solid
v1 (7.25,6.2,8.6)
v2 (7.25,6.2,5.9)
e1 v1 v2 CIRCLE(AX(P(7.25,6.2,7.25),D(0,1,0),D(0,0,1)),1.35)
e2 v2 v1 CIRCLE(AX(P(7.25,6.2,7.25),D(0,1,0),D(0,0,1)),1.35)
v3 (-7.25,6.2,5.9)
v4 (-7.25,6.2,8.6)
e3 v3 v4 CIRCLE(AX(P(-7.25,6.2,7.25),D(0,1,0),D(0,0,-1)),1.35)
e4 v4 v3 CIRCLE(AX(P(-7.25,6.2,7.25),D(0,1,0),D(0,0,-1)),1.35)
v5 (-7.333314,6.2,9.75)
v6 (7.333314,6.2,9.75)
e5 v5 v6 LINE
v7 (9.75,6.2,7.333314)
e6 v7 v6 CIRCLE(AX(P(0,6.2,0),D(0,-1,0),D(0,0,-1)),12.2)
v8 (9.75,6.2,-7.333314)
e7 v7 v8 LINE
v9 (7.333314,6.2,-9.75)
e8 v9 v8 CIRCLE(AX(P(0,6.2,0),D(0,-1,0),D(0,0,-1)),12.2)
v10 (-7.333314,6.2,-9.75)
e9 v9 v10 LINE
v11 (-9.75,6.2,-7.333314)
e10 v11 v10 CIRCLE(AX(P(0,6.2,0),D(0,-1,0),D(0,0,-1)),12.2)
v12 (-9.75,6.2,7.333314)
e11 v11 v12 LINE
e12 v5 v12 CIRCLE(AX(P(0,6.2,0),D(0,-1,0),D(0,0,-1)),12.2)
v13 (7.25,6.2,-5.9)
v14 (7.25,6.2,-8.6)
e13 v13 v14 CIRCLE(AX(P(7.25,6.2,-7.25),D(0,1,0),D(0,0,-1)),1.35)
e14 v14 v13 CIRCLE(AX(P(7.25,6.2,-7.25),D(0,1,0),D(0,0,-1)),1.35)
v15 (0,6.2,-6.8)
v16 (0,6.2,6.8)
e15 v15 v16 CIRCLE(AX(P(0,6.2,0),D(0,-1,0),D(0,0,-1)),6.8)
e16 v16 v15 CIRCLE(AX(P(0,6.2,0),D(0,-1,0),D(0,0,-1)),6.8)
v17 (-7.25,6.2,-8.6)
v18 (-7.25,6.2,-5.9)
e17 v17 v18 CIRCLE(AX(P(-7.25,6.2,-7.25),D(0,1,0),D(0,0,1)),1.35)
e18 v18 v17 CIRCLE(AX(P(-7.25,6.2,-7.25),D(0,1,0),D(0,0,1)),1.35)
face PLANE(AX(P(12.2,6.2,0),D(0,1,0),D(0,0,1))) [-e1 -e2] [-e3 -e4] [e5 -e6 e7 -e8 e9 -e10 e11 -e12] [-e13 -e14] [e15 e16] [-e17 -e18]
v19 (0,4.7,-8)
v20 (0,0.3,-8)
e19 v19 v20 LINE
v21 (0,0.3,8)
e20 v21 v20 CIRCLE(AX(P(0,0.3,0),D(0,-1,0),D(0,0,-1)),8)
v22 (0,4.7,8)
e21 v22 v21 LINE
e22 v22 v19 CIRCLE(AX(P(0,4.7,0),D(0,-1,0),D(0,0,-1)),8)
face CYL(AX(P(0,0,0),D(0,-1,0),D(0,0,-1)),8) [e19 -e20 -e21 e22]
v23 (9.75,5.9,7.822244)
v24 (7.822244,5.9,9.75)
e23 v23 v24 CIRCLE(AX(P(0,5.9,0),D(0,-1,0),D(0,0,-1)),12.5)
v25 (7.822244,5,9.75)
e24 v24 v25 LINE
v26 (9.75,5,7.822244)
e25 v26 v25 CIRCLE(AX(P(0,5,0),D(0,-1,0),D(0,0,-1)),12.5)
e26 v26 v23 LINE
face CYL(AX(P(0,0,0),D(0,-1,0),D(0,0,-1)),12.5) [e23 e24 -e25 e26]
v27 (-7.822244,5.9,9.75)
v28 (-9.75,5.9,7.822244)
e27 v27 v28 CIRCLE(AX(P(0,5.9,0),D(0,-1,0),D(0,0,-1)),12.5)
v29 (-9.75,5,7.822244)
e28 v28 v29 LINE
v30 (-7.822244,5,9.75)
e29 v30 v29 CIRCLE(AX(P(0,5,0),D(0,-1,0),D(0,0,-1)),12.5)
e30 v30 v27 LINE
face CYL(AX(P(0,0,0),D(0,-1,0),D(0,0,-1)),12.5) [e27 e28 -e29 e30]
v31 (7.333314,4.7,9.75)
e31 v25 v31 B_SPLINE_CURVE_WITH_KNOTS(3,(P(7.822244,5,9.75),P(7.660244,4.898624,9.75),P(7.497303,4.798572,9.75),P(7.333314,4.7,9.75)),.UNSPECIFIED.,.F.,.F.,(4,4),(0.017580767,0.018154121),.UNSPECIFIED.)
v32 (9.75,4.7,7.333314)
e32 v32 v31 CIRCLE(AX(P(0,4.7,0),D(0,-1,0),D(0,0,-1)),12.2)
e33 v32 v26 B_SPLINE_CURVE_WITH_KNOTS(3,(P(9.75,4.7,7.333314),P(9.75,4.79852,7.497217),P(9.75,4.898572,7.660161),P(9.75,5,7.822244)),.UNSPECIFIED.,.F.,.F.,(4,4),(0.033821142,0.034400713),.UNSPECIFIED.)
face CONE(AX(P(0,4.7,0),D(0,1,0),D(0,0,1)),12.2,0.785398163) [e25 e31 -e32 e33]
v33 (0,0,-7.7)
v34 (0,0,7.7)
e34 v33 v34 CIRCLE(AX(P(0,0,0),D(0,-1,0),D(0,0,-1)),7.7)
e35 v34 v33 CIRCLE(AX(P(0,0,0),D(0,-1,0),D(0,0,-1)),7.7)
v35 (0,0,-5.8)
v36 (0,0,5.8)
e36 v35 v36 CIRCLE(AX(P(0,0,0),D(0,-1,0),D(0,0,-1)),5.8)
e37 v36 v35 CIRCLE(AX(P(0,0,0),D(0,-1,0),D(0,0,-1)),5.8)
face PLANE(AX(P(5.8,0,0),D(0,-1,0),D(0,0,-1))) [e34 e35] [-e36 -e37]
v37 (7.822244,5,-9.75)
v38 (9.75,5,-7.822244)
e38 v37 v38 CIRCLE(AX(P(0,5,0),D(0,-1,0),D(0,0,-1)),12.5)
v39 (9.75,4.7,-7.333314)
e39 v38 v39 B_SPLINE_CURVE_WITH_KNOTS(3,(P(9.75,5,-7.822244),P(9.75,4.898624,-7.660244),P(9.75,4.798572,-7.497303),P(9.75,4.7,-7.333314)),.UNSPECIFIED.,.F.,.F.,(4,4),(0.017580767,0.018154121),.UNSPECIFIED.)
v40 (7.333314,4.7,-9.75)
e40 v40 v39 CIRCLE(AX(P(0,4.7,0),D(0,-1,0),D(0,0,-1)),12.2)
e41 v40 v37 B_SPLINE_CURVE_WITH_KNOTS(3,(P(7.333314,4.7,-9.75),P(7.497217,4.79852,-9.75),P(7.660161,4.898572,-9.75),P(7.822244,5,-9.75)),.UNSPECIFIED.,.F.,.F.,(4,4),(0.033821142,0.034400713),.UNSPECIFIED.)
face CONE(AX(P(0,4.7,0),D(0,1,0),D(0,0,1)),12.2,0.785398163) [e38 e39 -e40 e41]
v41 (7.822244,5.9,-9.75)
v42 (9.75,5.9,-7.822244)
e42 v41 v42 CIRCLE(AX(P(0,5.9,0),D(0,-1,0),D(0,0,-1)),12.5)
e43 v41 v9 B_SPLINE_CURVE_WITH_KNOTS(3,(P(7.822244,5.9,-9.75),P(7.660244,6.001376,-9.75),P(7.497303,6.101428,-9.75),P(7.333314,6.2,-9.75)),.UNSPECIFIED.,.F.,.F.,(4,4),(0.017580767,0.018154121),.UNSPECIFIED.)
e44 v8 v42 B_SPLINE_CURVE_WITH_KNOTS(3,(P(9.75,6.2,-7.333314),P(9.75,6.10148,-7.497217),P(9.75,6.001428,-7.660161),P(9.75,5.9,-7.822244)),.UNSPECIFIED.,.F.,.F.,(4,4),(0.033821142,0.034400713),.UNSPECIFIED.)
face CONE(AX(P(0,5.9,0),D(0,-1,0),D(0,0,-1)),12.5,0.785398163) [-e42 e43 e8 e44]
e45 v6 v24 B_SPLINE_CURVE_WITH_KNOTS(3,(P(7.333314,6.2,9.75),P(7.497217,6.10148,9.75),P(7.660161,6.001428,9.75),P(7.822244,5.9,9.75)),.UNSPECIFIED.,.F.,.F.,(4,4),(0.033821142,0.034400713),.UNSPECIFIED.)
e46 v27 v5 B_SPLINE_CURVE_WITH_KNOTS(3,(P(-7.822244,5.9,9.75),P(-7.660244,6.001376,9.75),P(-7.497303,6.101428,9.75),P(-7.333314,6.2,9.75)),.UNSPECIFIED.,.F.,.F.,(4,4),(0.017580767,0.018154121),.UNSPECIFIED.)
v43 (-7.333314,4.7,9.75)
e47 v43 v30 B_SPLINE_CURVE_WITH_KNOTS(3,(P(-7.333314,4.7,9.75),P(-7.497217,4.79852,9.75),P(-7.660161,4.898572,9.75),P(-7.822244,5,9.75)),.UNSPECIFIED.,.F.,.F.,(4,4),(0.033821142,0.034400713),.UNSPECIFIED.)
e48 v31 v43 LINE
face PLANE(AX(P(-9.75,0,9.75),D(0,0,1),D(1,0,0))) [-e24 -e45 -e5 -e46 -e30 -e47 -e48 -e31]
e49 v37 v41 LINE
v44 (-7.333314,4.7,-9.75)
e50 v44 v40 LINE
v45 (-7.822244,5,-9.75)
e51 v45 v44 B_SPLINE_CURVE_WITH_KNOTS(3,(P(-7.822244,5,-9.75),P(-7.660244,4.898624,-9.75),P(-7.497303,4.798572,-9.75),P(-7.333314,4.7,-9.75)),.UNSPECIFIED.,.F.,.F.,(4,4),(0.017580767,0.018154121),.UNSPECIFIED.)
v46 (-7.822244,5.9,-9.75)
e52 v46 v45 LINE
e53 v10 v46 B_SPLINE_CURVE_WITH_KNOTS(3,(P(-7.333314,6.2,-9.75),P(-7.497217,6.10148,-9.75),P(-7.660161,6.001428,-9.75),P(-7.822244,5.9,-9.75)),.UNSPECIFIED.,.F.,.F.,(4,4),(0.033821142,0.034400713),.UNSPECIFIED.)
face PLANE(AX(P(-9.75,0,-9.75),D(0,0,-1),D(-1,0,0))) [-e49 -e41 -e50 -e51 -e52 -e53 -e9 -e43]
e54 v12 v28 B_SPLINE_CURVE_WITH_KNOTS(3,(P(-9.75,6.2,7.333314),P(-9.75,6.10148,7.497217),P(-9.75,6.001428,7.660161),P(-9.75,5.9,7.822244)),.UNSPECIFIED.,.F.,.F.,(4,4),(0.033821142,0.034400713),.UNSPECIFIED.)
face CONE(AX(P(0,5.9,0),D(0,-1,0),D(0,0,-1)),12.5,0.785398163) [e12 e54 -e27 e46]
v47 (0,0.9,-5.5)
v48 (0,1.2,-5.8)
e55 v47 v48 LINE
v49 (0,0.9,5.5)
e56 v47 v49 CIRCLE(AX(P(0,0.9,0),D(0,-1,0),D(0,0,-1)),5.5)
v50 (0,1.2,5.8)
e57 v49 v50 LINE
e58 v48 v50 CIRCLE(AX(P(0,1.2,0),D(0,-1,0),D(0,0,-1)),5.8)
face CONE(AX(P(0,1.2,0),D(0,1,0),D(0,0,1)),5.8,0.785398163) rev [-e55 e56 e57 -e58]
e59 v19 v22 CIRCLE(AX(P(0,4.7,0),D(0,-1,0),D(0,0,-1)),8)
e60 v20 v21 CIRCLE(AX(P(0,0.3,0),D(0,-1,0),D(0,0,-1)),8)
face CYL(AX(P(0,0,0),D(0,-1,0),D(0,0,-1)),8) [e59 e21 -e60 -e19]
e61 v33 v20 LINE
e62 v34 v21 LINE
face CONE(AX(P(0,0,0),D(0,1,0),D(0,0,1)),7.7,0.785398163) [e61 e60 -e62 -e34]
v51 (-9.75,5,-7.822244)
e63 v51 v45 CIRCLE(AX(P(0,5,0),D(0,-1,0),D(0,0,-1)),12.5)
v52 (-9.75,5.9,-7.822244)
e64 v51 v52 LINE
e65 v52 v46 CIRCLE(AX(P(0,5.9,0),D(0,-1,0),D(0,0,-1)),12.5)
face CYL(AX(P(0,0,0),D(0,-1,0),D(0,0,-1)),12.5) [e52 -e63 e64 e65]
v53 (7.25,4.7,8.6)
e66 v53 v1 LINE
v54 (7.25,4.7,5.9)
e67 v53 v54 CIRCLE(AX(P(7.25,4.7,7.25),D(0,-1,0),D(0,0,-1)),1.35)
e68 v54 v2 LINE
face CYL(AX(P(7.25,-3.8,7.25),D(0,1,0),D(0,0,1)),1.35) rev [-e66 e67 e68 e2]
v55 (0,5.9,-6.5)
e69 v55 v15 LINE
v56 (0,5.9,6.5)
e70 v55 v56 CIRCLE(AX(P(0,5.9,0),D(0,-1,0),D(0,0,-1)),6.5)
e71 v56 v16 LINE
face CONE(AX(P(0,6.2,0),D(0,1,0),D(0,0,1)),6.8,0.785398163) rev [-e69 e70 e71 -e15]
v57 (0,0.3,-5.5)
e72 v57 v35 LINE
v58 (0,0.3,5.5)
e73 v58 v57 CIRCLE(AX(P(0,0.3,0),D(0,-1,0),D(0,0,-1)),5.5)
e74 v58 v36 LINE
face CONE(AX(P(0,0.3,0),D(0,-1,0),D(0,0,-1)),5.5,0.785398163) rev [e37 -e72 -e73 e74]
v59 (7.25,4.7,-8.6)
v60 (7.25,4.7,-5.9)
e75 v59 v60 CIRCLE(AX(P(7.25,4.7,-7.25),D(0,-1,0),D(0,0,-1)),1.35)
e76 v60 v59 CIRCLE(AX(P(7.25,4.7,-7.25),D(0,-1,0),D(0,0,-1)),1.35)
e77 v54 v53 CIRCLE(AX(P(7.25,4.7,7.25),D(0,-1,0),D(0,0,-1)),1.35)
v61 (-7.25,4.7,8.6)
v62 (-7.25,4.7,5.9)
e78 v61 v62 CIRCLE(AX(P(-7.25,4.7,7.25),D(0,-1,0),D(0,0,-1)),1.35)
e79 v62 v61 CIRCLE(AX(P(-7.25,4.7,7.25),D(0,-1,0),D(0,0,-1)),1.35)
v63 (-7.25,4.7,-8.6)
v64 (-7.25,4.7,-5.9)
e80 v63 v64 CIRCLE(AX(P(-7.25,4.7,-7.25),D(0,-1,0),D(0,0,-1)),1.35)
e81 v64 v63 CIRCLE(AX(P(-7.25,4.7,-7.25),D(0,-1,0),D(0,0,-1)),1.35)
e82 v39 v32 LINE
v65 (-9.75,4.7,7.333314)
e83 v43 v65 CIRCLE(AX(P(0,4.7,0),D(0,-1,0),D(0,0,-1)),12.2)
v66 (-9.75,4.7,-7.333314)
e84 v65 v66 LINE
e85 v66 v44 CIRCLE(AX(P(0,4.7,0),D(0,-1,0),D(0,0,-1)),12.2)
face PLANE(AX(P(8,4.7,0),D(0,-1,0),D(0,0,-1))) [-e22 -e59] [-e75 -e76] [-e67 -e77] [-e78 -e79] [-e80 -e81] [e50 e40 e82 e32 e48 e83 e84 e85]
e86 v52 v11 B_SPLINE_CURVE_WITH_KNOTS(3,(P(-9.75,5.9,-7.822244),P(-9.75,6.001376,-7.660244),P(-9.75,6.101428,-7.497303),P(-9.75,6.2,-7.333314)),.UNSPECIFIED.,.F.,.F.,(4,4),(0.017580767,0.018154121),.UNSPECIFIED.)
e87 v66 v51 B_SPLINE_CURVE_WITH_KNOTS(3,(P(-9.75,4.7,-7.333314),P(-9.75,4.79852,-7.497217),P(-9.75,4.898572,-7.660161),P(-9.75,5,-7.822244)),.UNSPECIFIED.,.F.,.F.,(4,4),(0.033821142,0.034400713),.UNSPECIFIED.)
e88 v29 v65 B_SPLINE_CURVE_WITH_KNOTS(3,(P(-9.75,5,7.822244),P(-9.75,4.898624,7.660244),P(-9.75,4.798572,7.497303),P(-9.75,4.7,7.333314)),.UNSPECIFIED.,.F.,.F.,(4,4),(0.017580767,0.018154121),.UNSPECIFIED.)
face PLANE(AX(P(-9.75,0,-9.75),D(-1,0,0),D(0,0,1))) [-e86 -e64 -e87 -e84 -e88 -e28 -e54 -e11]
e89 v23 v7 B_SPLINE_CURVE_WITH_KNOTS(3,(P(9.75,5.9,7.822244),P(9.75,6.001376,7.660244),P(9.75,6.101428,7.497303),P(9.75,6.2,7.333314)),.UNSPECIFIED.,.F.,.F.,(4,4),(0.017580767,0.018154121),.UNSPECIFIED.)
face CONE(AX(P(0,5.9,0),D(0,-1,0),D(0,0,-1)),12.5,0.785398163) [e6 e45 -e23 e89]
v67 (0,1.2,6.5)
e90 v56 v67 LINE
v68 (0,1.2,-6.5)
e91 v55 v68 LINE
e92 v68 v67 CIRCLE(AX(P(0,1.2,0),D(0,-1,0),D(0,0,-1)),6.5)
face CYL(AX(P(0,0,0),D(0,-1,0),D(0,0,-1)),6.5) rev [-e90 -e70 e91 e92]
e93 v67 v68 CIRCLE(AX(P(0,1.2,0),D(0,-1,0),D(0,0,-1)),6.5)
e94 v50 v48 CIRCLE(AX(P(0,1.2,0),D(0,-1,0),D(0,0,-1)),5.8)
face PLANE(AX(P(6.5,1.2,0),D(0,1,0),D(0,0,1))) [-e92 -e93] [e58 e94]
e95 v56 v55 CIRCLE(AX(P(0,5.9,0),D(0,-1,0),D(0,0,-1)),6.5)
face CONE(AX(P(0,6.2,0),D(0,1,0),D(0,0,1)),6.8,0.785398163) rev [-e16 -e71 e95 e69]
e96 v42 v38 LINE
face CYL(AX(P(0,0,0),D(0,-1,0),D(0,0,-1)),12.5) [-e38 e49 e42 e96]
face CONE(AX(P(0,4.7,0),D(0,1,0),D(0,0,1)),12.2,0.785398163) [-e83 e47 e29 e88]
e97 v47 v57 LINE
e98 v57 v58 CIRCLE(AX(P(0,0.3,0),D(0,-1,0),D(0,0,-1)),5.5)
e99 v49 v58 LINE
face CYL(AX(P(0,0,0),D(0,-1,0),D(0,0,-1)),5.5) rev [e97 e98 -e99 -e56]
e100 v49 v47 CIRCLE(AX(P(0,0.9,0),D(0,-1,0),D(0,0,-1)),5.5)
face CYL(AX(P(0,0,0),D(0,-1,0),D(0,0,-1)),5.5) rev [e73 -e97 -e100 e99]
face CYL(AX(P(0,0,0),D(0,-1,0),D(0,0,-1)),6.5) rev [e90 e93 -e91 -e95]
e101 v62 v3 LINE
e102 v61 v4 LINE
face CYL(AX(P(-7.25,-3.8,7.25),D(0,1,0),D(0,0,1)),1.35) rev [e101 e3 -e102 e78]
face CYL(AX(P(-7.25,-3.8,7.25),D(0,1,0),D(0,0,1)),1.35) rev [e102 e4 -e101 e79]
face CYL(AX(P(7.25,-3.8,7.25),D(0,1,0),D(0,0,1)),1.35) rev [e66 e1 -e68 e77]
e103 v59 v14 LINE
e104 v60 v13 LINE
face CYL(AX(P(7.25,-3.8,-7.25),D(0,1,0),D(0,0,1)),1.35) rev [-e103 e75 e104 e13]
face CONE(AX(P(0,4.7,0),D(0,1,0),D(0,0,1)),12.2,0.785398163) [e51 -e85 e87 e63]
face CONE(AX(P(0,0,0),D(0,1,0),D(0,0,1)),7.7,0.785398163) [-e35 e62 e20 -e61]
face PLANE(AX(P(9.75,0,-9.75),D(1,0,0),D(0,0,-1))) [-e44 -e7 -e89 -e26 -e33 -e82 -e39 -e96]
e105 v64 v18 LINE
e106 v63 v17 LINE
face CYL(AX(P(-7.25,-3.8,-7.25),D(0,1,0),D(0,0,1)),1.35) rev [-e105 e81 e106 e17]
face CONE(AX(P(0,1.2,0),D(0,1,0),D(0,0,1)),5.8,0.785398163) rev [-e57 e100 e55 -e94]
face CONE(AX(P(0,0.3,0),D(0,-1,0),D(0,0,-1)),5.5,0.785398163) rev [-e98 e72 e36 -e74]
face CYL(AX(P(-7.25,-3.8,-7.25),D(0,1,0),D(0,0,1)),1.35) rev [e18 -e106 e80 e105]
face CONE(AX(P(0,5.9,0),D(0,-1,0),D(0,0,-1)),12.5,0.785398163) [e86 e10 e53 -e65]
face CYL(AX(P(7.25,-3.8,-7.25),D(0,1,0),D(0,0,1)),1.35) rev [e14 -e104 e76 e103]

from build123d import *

# Parameters (mm, degrees)
SKETCH2_OUTSIDE_W   = 34.178
SKETCH2_OUTSIDE_H   = 34.178
SKETCH2_OUTSIDE_W_2 = 19.5
SKETCH2_OUTSIDE_H_2 = 19.5
CUT_EXTRUDE1_DEPTH  = 19.733392645
SKETCH3_R           = 1.35
CUT_EXTRUDE2_DEPTH  = 10


with BuildPart() as part:
    # Sketch1 → Revolve1 (revolve)
    with BuildSketch(Plane.XY, mode=Mode.PRIVATE) as revolve1_sk:
        Polygon((5.8, 0), (7.7, 0), (8, 0.3), (8, 4.7), (12.2, 4.7), (12.5, 5), (12.5, 5.9), (12.2, 6.2), (6.8, 6.2), (6.5, 5.9), (6.5, 1.2), (5.8, 1.2), (5.5, 0.9), (5.5, 0.3), align=None)
    revolve(revolve1_sk.sketch.rotate(Axis((0, 0, 0), (0, 1, 0)), 90), axis=Axis((0, 0, 0), (0, 1, 0)))

    # Sketch2 outside → Cut-Extrude1 (cut, through all)
    with BuildSketch(Plane(origin=(0, 6.2, 0), x_dir=(1, 0, 0), z_dir=(0, 1, 0))):
        Rectangle(SKETCH2_OUTSIDE_W, SKETCH2_OUTSIDE_H)
        Rectangle(SKETCH2_OUTSIDE_W_2, SKETCH2_OUTSIDE_H_2, mode=Mode.SUBTRACT)
    extrude(amount=-CUT_EXTRUDE1_DEPTH, mode=Mode.SUBTRACT)

    # Sketch3 → Cut-Extrude2 (cut)
    with BuildSketch(Plane(origin=(0, 6.2, 0), x_dir=(1, 0, 0), z_dir=(0, 1, 0))):
        with Locations(Location((-7.25, 7.25, 0), (0, 0, 270))):
            Circle(SKETCH3_R)
        with Locations(Location((7.25, 7.25, 0), (0, 0, 90))):
            Circle(SKETCH3_R)
        with Locations(Location((7.25, -7.25, 0), (0, 0, 270))):
            Circle(SKETCH3_R)
        with Locations(Location((-7.25, -7.25, 0), (0, 0, 90))):
            Circle(SKETCH3_R)
    extrude(amount=-CUT_EXTRUDE2_DEPTH, mode=Mode.SUBTRACT)


solid = part.part
